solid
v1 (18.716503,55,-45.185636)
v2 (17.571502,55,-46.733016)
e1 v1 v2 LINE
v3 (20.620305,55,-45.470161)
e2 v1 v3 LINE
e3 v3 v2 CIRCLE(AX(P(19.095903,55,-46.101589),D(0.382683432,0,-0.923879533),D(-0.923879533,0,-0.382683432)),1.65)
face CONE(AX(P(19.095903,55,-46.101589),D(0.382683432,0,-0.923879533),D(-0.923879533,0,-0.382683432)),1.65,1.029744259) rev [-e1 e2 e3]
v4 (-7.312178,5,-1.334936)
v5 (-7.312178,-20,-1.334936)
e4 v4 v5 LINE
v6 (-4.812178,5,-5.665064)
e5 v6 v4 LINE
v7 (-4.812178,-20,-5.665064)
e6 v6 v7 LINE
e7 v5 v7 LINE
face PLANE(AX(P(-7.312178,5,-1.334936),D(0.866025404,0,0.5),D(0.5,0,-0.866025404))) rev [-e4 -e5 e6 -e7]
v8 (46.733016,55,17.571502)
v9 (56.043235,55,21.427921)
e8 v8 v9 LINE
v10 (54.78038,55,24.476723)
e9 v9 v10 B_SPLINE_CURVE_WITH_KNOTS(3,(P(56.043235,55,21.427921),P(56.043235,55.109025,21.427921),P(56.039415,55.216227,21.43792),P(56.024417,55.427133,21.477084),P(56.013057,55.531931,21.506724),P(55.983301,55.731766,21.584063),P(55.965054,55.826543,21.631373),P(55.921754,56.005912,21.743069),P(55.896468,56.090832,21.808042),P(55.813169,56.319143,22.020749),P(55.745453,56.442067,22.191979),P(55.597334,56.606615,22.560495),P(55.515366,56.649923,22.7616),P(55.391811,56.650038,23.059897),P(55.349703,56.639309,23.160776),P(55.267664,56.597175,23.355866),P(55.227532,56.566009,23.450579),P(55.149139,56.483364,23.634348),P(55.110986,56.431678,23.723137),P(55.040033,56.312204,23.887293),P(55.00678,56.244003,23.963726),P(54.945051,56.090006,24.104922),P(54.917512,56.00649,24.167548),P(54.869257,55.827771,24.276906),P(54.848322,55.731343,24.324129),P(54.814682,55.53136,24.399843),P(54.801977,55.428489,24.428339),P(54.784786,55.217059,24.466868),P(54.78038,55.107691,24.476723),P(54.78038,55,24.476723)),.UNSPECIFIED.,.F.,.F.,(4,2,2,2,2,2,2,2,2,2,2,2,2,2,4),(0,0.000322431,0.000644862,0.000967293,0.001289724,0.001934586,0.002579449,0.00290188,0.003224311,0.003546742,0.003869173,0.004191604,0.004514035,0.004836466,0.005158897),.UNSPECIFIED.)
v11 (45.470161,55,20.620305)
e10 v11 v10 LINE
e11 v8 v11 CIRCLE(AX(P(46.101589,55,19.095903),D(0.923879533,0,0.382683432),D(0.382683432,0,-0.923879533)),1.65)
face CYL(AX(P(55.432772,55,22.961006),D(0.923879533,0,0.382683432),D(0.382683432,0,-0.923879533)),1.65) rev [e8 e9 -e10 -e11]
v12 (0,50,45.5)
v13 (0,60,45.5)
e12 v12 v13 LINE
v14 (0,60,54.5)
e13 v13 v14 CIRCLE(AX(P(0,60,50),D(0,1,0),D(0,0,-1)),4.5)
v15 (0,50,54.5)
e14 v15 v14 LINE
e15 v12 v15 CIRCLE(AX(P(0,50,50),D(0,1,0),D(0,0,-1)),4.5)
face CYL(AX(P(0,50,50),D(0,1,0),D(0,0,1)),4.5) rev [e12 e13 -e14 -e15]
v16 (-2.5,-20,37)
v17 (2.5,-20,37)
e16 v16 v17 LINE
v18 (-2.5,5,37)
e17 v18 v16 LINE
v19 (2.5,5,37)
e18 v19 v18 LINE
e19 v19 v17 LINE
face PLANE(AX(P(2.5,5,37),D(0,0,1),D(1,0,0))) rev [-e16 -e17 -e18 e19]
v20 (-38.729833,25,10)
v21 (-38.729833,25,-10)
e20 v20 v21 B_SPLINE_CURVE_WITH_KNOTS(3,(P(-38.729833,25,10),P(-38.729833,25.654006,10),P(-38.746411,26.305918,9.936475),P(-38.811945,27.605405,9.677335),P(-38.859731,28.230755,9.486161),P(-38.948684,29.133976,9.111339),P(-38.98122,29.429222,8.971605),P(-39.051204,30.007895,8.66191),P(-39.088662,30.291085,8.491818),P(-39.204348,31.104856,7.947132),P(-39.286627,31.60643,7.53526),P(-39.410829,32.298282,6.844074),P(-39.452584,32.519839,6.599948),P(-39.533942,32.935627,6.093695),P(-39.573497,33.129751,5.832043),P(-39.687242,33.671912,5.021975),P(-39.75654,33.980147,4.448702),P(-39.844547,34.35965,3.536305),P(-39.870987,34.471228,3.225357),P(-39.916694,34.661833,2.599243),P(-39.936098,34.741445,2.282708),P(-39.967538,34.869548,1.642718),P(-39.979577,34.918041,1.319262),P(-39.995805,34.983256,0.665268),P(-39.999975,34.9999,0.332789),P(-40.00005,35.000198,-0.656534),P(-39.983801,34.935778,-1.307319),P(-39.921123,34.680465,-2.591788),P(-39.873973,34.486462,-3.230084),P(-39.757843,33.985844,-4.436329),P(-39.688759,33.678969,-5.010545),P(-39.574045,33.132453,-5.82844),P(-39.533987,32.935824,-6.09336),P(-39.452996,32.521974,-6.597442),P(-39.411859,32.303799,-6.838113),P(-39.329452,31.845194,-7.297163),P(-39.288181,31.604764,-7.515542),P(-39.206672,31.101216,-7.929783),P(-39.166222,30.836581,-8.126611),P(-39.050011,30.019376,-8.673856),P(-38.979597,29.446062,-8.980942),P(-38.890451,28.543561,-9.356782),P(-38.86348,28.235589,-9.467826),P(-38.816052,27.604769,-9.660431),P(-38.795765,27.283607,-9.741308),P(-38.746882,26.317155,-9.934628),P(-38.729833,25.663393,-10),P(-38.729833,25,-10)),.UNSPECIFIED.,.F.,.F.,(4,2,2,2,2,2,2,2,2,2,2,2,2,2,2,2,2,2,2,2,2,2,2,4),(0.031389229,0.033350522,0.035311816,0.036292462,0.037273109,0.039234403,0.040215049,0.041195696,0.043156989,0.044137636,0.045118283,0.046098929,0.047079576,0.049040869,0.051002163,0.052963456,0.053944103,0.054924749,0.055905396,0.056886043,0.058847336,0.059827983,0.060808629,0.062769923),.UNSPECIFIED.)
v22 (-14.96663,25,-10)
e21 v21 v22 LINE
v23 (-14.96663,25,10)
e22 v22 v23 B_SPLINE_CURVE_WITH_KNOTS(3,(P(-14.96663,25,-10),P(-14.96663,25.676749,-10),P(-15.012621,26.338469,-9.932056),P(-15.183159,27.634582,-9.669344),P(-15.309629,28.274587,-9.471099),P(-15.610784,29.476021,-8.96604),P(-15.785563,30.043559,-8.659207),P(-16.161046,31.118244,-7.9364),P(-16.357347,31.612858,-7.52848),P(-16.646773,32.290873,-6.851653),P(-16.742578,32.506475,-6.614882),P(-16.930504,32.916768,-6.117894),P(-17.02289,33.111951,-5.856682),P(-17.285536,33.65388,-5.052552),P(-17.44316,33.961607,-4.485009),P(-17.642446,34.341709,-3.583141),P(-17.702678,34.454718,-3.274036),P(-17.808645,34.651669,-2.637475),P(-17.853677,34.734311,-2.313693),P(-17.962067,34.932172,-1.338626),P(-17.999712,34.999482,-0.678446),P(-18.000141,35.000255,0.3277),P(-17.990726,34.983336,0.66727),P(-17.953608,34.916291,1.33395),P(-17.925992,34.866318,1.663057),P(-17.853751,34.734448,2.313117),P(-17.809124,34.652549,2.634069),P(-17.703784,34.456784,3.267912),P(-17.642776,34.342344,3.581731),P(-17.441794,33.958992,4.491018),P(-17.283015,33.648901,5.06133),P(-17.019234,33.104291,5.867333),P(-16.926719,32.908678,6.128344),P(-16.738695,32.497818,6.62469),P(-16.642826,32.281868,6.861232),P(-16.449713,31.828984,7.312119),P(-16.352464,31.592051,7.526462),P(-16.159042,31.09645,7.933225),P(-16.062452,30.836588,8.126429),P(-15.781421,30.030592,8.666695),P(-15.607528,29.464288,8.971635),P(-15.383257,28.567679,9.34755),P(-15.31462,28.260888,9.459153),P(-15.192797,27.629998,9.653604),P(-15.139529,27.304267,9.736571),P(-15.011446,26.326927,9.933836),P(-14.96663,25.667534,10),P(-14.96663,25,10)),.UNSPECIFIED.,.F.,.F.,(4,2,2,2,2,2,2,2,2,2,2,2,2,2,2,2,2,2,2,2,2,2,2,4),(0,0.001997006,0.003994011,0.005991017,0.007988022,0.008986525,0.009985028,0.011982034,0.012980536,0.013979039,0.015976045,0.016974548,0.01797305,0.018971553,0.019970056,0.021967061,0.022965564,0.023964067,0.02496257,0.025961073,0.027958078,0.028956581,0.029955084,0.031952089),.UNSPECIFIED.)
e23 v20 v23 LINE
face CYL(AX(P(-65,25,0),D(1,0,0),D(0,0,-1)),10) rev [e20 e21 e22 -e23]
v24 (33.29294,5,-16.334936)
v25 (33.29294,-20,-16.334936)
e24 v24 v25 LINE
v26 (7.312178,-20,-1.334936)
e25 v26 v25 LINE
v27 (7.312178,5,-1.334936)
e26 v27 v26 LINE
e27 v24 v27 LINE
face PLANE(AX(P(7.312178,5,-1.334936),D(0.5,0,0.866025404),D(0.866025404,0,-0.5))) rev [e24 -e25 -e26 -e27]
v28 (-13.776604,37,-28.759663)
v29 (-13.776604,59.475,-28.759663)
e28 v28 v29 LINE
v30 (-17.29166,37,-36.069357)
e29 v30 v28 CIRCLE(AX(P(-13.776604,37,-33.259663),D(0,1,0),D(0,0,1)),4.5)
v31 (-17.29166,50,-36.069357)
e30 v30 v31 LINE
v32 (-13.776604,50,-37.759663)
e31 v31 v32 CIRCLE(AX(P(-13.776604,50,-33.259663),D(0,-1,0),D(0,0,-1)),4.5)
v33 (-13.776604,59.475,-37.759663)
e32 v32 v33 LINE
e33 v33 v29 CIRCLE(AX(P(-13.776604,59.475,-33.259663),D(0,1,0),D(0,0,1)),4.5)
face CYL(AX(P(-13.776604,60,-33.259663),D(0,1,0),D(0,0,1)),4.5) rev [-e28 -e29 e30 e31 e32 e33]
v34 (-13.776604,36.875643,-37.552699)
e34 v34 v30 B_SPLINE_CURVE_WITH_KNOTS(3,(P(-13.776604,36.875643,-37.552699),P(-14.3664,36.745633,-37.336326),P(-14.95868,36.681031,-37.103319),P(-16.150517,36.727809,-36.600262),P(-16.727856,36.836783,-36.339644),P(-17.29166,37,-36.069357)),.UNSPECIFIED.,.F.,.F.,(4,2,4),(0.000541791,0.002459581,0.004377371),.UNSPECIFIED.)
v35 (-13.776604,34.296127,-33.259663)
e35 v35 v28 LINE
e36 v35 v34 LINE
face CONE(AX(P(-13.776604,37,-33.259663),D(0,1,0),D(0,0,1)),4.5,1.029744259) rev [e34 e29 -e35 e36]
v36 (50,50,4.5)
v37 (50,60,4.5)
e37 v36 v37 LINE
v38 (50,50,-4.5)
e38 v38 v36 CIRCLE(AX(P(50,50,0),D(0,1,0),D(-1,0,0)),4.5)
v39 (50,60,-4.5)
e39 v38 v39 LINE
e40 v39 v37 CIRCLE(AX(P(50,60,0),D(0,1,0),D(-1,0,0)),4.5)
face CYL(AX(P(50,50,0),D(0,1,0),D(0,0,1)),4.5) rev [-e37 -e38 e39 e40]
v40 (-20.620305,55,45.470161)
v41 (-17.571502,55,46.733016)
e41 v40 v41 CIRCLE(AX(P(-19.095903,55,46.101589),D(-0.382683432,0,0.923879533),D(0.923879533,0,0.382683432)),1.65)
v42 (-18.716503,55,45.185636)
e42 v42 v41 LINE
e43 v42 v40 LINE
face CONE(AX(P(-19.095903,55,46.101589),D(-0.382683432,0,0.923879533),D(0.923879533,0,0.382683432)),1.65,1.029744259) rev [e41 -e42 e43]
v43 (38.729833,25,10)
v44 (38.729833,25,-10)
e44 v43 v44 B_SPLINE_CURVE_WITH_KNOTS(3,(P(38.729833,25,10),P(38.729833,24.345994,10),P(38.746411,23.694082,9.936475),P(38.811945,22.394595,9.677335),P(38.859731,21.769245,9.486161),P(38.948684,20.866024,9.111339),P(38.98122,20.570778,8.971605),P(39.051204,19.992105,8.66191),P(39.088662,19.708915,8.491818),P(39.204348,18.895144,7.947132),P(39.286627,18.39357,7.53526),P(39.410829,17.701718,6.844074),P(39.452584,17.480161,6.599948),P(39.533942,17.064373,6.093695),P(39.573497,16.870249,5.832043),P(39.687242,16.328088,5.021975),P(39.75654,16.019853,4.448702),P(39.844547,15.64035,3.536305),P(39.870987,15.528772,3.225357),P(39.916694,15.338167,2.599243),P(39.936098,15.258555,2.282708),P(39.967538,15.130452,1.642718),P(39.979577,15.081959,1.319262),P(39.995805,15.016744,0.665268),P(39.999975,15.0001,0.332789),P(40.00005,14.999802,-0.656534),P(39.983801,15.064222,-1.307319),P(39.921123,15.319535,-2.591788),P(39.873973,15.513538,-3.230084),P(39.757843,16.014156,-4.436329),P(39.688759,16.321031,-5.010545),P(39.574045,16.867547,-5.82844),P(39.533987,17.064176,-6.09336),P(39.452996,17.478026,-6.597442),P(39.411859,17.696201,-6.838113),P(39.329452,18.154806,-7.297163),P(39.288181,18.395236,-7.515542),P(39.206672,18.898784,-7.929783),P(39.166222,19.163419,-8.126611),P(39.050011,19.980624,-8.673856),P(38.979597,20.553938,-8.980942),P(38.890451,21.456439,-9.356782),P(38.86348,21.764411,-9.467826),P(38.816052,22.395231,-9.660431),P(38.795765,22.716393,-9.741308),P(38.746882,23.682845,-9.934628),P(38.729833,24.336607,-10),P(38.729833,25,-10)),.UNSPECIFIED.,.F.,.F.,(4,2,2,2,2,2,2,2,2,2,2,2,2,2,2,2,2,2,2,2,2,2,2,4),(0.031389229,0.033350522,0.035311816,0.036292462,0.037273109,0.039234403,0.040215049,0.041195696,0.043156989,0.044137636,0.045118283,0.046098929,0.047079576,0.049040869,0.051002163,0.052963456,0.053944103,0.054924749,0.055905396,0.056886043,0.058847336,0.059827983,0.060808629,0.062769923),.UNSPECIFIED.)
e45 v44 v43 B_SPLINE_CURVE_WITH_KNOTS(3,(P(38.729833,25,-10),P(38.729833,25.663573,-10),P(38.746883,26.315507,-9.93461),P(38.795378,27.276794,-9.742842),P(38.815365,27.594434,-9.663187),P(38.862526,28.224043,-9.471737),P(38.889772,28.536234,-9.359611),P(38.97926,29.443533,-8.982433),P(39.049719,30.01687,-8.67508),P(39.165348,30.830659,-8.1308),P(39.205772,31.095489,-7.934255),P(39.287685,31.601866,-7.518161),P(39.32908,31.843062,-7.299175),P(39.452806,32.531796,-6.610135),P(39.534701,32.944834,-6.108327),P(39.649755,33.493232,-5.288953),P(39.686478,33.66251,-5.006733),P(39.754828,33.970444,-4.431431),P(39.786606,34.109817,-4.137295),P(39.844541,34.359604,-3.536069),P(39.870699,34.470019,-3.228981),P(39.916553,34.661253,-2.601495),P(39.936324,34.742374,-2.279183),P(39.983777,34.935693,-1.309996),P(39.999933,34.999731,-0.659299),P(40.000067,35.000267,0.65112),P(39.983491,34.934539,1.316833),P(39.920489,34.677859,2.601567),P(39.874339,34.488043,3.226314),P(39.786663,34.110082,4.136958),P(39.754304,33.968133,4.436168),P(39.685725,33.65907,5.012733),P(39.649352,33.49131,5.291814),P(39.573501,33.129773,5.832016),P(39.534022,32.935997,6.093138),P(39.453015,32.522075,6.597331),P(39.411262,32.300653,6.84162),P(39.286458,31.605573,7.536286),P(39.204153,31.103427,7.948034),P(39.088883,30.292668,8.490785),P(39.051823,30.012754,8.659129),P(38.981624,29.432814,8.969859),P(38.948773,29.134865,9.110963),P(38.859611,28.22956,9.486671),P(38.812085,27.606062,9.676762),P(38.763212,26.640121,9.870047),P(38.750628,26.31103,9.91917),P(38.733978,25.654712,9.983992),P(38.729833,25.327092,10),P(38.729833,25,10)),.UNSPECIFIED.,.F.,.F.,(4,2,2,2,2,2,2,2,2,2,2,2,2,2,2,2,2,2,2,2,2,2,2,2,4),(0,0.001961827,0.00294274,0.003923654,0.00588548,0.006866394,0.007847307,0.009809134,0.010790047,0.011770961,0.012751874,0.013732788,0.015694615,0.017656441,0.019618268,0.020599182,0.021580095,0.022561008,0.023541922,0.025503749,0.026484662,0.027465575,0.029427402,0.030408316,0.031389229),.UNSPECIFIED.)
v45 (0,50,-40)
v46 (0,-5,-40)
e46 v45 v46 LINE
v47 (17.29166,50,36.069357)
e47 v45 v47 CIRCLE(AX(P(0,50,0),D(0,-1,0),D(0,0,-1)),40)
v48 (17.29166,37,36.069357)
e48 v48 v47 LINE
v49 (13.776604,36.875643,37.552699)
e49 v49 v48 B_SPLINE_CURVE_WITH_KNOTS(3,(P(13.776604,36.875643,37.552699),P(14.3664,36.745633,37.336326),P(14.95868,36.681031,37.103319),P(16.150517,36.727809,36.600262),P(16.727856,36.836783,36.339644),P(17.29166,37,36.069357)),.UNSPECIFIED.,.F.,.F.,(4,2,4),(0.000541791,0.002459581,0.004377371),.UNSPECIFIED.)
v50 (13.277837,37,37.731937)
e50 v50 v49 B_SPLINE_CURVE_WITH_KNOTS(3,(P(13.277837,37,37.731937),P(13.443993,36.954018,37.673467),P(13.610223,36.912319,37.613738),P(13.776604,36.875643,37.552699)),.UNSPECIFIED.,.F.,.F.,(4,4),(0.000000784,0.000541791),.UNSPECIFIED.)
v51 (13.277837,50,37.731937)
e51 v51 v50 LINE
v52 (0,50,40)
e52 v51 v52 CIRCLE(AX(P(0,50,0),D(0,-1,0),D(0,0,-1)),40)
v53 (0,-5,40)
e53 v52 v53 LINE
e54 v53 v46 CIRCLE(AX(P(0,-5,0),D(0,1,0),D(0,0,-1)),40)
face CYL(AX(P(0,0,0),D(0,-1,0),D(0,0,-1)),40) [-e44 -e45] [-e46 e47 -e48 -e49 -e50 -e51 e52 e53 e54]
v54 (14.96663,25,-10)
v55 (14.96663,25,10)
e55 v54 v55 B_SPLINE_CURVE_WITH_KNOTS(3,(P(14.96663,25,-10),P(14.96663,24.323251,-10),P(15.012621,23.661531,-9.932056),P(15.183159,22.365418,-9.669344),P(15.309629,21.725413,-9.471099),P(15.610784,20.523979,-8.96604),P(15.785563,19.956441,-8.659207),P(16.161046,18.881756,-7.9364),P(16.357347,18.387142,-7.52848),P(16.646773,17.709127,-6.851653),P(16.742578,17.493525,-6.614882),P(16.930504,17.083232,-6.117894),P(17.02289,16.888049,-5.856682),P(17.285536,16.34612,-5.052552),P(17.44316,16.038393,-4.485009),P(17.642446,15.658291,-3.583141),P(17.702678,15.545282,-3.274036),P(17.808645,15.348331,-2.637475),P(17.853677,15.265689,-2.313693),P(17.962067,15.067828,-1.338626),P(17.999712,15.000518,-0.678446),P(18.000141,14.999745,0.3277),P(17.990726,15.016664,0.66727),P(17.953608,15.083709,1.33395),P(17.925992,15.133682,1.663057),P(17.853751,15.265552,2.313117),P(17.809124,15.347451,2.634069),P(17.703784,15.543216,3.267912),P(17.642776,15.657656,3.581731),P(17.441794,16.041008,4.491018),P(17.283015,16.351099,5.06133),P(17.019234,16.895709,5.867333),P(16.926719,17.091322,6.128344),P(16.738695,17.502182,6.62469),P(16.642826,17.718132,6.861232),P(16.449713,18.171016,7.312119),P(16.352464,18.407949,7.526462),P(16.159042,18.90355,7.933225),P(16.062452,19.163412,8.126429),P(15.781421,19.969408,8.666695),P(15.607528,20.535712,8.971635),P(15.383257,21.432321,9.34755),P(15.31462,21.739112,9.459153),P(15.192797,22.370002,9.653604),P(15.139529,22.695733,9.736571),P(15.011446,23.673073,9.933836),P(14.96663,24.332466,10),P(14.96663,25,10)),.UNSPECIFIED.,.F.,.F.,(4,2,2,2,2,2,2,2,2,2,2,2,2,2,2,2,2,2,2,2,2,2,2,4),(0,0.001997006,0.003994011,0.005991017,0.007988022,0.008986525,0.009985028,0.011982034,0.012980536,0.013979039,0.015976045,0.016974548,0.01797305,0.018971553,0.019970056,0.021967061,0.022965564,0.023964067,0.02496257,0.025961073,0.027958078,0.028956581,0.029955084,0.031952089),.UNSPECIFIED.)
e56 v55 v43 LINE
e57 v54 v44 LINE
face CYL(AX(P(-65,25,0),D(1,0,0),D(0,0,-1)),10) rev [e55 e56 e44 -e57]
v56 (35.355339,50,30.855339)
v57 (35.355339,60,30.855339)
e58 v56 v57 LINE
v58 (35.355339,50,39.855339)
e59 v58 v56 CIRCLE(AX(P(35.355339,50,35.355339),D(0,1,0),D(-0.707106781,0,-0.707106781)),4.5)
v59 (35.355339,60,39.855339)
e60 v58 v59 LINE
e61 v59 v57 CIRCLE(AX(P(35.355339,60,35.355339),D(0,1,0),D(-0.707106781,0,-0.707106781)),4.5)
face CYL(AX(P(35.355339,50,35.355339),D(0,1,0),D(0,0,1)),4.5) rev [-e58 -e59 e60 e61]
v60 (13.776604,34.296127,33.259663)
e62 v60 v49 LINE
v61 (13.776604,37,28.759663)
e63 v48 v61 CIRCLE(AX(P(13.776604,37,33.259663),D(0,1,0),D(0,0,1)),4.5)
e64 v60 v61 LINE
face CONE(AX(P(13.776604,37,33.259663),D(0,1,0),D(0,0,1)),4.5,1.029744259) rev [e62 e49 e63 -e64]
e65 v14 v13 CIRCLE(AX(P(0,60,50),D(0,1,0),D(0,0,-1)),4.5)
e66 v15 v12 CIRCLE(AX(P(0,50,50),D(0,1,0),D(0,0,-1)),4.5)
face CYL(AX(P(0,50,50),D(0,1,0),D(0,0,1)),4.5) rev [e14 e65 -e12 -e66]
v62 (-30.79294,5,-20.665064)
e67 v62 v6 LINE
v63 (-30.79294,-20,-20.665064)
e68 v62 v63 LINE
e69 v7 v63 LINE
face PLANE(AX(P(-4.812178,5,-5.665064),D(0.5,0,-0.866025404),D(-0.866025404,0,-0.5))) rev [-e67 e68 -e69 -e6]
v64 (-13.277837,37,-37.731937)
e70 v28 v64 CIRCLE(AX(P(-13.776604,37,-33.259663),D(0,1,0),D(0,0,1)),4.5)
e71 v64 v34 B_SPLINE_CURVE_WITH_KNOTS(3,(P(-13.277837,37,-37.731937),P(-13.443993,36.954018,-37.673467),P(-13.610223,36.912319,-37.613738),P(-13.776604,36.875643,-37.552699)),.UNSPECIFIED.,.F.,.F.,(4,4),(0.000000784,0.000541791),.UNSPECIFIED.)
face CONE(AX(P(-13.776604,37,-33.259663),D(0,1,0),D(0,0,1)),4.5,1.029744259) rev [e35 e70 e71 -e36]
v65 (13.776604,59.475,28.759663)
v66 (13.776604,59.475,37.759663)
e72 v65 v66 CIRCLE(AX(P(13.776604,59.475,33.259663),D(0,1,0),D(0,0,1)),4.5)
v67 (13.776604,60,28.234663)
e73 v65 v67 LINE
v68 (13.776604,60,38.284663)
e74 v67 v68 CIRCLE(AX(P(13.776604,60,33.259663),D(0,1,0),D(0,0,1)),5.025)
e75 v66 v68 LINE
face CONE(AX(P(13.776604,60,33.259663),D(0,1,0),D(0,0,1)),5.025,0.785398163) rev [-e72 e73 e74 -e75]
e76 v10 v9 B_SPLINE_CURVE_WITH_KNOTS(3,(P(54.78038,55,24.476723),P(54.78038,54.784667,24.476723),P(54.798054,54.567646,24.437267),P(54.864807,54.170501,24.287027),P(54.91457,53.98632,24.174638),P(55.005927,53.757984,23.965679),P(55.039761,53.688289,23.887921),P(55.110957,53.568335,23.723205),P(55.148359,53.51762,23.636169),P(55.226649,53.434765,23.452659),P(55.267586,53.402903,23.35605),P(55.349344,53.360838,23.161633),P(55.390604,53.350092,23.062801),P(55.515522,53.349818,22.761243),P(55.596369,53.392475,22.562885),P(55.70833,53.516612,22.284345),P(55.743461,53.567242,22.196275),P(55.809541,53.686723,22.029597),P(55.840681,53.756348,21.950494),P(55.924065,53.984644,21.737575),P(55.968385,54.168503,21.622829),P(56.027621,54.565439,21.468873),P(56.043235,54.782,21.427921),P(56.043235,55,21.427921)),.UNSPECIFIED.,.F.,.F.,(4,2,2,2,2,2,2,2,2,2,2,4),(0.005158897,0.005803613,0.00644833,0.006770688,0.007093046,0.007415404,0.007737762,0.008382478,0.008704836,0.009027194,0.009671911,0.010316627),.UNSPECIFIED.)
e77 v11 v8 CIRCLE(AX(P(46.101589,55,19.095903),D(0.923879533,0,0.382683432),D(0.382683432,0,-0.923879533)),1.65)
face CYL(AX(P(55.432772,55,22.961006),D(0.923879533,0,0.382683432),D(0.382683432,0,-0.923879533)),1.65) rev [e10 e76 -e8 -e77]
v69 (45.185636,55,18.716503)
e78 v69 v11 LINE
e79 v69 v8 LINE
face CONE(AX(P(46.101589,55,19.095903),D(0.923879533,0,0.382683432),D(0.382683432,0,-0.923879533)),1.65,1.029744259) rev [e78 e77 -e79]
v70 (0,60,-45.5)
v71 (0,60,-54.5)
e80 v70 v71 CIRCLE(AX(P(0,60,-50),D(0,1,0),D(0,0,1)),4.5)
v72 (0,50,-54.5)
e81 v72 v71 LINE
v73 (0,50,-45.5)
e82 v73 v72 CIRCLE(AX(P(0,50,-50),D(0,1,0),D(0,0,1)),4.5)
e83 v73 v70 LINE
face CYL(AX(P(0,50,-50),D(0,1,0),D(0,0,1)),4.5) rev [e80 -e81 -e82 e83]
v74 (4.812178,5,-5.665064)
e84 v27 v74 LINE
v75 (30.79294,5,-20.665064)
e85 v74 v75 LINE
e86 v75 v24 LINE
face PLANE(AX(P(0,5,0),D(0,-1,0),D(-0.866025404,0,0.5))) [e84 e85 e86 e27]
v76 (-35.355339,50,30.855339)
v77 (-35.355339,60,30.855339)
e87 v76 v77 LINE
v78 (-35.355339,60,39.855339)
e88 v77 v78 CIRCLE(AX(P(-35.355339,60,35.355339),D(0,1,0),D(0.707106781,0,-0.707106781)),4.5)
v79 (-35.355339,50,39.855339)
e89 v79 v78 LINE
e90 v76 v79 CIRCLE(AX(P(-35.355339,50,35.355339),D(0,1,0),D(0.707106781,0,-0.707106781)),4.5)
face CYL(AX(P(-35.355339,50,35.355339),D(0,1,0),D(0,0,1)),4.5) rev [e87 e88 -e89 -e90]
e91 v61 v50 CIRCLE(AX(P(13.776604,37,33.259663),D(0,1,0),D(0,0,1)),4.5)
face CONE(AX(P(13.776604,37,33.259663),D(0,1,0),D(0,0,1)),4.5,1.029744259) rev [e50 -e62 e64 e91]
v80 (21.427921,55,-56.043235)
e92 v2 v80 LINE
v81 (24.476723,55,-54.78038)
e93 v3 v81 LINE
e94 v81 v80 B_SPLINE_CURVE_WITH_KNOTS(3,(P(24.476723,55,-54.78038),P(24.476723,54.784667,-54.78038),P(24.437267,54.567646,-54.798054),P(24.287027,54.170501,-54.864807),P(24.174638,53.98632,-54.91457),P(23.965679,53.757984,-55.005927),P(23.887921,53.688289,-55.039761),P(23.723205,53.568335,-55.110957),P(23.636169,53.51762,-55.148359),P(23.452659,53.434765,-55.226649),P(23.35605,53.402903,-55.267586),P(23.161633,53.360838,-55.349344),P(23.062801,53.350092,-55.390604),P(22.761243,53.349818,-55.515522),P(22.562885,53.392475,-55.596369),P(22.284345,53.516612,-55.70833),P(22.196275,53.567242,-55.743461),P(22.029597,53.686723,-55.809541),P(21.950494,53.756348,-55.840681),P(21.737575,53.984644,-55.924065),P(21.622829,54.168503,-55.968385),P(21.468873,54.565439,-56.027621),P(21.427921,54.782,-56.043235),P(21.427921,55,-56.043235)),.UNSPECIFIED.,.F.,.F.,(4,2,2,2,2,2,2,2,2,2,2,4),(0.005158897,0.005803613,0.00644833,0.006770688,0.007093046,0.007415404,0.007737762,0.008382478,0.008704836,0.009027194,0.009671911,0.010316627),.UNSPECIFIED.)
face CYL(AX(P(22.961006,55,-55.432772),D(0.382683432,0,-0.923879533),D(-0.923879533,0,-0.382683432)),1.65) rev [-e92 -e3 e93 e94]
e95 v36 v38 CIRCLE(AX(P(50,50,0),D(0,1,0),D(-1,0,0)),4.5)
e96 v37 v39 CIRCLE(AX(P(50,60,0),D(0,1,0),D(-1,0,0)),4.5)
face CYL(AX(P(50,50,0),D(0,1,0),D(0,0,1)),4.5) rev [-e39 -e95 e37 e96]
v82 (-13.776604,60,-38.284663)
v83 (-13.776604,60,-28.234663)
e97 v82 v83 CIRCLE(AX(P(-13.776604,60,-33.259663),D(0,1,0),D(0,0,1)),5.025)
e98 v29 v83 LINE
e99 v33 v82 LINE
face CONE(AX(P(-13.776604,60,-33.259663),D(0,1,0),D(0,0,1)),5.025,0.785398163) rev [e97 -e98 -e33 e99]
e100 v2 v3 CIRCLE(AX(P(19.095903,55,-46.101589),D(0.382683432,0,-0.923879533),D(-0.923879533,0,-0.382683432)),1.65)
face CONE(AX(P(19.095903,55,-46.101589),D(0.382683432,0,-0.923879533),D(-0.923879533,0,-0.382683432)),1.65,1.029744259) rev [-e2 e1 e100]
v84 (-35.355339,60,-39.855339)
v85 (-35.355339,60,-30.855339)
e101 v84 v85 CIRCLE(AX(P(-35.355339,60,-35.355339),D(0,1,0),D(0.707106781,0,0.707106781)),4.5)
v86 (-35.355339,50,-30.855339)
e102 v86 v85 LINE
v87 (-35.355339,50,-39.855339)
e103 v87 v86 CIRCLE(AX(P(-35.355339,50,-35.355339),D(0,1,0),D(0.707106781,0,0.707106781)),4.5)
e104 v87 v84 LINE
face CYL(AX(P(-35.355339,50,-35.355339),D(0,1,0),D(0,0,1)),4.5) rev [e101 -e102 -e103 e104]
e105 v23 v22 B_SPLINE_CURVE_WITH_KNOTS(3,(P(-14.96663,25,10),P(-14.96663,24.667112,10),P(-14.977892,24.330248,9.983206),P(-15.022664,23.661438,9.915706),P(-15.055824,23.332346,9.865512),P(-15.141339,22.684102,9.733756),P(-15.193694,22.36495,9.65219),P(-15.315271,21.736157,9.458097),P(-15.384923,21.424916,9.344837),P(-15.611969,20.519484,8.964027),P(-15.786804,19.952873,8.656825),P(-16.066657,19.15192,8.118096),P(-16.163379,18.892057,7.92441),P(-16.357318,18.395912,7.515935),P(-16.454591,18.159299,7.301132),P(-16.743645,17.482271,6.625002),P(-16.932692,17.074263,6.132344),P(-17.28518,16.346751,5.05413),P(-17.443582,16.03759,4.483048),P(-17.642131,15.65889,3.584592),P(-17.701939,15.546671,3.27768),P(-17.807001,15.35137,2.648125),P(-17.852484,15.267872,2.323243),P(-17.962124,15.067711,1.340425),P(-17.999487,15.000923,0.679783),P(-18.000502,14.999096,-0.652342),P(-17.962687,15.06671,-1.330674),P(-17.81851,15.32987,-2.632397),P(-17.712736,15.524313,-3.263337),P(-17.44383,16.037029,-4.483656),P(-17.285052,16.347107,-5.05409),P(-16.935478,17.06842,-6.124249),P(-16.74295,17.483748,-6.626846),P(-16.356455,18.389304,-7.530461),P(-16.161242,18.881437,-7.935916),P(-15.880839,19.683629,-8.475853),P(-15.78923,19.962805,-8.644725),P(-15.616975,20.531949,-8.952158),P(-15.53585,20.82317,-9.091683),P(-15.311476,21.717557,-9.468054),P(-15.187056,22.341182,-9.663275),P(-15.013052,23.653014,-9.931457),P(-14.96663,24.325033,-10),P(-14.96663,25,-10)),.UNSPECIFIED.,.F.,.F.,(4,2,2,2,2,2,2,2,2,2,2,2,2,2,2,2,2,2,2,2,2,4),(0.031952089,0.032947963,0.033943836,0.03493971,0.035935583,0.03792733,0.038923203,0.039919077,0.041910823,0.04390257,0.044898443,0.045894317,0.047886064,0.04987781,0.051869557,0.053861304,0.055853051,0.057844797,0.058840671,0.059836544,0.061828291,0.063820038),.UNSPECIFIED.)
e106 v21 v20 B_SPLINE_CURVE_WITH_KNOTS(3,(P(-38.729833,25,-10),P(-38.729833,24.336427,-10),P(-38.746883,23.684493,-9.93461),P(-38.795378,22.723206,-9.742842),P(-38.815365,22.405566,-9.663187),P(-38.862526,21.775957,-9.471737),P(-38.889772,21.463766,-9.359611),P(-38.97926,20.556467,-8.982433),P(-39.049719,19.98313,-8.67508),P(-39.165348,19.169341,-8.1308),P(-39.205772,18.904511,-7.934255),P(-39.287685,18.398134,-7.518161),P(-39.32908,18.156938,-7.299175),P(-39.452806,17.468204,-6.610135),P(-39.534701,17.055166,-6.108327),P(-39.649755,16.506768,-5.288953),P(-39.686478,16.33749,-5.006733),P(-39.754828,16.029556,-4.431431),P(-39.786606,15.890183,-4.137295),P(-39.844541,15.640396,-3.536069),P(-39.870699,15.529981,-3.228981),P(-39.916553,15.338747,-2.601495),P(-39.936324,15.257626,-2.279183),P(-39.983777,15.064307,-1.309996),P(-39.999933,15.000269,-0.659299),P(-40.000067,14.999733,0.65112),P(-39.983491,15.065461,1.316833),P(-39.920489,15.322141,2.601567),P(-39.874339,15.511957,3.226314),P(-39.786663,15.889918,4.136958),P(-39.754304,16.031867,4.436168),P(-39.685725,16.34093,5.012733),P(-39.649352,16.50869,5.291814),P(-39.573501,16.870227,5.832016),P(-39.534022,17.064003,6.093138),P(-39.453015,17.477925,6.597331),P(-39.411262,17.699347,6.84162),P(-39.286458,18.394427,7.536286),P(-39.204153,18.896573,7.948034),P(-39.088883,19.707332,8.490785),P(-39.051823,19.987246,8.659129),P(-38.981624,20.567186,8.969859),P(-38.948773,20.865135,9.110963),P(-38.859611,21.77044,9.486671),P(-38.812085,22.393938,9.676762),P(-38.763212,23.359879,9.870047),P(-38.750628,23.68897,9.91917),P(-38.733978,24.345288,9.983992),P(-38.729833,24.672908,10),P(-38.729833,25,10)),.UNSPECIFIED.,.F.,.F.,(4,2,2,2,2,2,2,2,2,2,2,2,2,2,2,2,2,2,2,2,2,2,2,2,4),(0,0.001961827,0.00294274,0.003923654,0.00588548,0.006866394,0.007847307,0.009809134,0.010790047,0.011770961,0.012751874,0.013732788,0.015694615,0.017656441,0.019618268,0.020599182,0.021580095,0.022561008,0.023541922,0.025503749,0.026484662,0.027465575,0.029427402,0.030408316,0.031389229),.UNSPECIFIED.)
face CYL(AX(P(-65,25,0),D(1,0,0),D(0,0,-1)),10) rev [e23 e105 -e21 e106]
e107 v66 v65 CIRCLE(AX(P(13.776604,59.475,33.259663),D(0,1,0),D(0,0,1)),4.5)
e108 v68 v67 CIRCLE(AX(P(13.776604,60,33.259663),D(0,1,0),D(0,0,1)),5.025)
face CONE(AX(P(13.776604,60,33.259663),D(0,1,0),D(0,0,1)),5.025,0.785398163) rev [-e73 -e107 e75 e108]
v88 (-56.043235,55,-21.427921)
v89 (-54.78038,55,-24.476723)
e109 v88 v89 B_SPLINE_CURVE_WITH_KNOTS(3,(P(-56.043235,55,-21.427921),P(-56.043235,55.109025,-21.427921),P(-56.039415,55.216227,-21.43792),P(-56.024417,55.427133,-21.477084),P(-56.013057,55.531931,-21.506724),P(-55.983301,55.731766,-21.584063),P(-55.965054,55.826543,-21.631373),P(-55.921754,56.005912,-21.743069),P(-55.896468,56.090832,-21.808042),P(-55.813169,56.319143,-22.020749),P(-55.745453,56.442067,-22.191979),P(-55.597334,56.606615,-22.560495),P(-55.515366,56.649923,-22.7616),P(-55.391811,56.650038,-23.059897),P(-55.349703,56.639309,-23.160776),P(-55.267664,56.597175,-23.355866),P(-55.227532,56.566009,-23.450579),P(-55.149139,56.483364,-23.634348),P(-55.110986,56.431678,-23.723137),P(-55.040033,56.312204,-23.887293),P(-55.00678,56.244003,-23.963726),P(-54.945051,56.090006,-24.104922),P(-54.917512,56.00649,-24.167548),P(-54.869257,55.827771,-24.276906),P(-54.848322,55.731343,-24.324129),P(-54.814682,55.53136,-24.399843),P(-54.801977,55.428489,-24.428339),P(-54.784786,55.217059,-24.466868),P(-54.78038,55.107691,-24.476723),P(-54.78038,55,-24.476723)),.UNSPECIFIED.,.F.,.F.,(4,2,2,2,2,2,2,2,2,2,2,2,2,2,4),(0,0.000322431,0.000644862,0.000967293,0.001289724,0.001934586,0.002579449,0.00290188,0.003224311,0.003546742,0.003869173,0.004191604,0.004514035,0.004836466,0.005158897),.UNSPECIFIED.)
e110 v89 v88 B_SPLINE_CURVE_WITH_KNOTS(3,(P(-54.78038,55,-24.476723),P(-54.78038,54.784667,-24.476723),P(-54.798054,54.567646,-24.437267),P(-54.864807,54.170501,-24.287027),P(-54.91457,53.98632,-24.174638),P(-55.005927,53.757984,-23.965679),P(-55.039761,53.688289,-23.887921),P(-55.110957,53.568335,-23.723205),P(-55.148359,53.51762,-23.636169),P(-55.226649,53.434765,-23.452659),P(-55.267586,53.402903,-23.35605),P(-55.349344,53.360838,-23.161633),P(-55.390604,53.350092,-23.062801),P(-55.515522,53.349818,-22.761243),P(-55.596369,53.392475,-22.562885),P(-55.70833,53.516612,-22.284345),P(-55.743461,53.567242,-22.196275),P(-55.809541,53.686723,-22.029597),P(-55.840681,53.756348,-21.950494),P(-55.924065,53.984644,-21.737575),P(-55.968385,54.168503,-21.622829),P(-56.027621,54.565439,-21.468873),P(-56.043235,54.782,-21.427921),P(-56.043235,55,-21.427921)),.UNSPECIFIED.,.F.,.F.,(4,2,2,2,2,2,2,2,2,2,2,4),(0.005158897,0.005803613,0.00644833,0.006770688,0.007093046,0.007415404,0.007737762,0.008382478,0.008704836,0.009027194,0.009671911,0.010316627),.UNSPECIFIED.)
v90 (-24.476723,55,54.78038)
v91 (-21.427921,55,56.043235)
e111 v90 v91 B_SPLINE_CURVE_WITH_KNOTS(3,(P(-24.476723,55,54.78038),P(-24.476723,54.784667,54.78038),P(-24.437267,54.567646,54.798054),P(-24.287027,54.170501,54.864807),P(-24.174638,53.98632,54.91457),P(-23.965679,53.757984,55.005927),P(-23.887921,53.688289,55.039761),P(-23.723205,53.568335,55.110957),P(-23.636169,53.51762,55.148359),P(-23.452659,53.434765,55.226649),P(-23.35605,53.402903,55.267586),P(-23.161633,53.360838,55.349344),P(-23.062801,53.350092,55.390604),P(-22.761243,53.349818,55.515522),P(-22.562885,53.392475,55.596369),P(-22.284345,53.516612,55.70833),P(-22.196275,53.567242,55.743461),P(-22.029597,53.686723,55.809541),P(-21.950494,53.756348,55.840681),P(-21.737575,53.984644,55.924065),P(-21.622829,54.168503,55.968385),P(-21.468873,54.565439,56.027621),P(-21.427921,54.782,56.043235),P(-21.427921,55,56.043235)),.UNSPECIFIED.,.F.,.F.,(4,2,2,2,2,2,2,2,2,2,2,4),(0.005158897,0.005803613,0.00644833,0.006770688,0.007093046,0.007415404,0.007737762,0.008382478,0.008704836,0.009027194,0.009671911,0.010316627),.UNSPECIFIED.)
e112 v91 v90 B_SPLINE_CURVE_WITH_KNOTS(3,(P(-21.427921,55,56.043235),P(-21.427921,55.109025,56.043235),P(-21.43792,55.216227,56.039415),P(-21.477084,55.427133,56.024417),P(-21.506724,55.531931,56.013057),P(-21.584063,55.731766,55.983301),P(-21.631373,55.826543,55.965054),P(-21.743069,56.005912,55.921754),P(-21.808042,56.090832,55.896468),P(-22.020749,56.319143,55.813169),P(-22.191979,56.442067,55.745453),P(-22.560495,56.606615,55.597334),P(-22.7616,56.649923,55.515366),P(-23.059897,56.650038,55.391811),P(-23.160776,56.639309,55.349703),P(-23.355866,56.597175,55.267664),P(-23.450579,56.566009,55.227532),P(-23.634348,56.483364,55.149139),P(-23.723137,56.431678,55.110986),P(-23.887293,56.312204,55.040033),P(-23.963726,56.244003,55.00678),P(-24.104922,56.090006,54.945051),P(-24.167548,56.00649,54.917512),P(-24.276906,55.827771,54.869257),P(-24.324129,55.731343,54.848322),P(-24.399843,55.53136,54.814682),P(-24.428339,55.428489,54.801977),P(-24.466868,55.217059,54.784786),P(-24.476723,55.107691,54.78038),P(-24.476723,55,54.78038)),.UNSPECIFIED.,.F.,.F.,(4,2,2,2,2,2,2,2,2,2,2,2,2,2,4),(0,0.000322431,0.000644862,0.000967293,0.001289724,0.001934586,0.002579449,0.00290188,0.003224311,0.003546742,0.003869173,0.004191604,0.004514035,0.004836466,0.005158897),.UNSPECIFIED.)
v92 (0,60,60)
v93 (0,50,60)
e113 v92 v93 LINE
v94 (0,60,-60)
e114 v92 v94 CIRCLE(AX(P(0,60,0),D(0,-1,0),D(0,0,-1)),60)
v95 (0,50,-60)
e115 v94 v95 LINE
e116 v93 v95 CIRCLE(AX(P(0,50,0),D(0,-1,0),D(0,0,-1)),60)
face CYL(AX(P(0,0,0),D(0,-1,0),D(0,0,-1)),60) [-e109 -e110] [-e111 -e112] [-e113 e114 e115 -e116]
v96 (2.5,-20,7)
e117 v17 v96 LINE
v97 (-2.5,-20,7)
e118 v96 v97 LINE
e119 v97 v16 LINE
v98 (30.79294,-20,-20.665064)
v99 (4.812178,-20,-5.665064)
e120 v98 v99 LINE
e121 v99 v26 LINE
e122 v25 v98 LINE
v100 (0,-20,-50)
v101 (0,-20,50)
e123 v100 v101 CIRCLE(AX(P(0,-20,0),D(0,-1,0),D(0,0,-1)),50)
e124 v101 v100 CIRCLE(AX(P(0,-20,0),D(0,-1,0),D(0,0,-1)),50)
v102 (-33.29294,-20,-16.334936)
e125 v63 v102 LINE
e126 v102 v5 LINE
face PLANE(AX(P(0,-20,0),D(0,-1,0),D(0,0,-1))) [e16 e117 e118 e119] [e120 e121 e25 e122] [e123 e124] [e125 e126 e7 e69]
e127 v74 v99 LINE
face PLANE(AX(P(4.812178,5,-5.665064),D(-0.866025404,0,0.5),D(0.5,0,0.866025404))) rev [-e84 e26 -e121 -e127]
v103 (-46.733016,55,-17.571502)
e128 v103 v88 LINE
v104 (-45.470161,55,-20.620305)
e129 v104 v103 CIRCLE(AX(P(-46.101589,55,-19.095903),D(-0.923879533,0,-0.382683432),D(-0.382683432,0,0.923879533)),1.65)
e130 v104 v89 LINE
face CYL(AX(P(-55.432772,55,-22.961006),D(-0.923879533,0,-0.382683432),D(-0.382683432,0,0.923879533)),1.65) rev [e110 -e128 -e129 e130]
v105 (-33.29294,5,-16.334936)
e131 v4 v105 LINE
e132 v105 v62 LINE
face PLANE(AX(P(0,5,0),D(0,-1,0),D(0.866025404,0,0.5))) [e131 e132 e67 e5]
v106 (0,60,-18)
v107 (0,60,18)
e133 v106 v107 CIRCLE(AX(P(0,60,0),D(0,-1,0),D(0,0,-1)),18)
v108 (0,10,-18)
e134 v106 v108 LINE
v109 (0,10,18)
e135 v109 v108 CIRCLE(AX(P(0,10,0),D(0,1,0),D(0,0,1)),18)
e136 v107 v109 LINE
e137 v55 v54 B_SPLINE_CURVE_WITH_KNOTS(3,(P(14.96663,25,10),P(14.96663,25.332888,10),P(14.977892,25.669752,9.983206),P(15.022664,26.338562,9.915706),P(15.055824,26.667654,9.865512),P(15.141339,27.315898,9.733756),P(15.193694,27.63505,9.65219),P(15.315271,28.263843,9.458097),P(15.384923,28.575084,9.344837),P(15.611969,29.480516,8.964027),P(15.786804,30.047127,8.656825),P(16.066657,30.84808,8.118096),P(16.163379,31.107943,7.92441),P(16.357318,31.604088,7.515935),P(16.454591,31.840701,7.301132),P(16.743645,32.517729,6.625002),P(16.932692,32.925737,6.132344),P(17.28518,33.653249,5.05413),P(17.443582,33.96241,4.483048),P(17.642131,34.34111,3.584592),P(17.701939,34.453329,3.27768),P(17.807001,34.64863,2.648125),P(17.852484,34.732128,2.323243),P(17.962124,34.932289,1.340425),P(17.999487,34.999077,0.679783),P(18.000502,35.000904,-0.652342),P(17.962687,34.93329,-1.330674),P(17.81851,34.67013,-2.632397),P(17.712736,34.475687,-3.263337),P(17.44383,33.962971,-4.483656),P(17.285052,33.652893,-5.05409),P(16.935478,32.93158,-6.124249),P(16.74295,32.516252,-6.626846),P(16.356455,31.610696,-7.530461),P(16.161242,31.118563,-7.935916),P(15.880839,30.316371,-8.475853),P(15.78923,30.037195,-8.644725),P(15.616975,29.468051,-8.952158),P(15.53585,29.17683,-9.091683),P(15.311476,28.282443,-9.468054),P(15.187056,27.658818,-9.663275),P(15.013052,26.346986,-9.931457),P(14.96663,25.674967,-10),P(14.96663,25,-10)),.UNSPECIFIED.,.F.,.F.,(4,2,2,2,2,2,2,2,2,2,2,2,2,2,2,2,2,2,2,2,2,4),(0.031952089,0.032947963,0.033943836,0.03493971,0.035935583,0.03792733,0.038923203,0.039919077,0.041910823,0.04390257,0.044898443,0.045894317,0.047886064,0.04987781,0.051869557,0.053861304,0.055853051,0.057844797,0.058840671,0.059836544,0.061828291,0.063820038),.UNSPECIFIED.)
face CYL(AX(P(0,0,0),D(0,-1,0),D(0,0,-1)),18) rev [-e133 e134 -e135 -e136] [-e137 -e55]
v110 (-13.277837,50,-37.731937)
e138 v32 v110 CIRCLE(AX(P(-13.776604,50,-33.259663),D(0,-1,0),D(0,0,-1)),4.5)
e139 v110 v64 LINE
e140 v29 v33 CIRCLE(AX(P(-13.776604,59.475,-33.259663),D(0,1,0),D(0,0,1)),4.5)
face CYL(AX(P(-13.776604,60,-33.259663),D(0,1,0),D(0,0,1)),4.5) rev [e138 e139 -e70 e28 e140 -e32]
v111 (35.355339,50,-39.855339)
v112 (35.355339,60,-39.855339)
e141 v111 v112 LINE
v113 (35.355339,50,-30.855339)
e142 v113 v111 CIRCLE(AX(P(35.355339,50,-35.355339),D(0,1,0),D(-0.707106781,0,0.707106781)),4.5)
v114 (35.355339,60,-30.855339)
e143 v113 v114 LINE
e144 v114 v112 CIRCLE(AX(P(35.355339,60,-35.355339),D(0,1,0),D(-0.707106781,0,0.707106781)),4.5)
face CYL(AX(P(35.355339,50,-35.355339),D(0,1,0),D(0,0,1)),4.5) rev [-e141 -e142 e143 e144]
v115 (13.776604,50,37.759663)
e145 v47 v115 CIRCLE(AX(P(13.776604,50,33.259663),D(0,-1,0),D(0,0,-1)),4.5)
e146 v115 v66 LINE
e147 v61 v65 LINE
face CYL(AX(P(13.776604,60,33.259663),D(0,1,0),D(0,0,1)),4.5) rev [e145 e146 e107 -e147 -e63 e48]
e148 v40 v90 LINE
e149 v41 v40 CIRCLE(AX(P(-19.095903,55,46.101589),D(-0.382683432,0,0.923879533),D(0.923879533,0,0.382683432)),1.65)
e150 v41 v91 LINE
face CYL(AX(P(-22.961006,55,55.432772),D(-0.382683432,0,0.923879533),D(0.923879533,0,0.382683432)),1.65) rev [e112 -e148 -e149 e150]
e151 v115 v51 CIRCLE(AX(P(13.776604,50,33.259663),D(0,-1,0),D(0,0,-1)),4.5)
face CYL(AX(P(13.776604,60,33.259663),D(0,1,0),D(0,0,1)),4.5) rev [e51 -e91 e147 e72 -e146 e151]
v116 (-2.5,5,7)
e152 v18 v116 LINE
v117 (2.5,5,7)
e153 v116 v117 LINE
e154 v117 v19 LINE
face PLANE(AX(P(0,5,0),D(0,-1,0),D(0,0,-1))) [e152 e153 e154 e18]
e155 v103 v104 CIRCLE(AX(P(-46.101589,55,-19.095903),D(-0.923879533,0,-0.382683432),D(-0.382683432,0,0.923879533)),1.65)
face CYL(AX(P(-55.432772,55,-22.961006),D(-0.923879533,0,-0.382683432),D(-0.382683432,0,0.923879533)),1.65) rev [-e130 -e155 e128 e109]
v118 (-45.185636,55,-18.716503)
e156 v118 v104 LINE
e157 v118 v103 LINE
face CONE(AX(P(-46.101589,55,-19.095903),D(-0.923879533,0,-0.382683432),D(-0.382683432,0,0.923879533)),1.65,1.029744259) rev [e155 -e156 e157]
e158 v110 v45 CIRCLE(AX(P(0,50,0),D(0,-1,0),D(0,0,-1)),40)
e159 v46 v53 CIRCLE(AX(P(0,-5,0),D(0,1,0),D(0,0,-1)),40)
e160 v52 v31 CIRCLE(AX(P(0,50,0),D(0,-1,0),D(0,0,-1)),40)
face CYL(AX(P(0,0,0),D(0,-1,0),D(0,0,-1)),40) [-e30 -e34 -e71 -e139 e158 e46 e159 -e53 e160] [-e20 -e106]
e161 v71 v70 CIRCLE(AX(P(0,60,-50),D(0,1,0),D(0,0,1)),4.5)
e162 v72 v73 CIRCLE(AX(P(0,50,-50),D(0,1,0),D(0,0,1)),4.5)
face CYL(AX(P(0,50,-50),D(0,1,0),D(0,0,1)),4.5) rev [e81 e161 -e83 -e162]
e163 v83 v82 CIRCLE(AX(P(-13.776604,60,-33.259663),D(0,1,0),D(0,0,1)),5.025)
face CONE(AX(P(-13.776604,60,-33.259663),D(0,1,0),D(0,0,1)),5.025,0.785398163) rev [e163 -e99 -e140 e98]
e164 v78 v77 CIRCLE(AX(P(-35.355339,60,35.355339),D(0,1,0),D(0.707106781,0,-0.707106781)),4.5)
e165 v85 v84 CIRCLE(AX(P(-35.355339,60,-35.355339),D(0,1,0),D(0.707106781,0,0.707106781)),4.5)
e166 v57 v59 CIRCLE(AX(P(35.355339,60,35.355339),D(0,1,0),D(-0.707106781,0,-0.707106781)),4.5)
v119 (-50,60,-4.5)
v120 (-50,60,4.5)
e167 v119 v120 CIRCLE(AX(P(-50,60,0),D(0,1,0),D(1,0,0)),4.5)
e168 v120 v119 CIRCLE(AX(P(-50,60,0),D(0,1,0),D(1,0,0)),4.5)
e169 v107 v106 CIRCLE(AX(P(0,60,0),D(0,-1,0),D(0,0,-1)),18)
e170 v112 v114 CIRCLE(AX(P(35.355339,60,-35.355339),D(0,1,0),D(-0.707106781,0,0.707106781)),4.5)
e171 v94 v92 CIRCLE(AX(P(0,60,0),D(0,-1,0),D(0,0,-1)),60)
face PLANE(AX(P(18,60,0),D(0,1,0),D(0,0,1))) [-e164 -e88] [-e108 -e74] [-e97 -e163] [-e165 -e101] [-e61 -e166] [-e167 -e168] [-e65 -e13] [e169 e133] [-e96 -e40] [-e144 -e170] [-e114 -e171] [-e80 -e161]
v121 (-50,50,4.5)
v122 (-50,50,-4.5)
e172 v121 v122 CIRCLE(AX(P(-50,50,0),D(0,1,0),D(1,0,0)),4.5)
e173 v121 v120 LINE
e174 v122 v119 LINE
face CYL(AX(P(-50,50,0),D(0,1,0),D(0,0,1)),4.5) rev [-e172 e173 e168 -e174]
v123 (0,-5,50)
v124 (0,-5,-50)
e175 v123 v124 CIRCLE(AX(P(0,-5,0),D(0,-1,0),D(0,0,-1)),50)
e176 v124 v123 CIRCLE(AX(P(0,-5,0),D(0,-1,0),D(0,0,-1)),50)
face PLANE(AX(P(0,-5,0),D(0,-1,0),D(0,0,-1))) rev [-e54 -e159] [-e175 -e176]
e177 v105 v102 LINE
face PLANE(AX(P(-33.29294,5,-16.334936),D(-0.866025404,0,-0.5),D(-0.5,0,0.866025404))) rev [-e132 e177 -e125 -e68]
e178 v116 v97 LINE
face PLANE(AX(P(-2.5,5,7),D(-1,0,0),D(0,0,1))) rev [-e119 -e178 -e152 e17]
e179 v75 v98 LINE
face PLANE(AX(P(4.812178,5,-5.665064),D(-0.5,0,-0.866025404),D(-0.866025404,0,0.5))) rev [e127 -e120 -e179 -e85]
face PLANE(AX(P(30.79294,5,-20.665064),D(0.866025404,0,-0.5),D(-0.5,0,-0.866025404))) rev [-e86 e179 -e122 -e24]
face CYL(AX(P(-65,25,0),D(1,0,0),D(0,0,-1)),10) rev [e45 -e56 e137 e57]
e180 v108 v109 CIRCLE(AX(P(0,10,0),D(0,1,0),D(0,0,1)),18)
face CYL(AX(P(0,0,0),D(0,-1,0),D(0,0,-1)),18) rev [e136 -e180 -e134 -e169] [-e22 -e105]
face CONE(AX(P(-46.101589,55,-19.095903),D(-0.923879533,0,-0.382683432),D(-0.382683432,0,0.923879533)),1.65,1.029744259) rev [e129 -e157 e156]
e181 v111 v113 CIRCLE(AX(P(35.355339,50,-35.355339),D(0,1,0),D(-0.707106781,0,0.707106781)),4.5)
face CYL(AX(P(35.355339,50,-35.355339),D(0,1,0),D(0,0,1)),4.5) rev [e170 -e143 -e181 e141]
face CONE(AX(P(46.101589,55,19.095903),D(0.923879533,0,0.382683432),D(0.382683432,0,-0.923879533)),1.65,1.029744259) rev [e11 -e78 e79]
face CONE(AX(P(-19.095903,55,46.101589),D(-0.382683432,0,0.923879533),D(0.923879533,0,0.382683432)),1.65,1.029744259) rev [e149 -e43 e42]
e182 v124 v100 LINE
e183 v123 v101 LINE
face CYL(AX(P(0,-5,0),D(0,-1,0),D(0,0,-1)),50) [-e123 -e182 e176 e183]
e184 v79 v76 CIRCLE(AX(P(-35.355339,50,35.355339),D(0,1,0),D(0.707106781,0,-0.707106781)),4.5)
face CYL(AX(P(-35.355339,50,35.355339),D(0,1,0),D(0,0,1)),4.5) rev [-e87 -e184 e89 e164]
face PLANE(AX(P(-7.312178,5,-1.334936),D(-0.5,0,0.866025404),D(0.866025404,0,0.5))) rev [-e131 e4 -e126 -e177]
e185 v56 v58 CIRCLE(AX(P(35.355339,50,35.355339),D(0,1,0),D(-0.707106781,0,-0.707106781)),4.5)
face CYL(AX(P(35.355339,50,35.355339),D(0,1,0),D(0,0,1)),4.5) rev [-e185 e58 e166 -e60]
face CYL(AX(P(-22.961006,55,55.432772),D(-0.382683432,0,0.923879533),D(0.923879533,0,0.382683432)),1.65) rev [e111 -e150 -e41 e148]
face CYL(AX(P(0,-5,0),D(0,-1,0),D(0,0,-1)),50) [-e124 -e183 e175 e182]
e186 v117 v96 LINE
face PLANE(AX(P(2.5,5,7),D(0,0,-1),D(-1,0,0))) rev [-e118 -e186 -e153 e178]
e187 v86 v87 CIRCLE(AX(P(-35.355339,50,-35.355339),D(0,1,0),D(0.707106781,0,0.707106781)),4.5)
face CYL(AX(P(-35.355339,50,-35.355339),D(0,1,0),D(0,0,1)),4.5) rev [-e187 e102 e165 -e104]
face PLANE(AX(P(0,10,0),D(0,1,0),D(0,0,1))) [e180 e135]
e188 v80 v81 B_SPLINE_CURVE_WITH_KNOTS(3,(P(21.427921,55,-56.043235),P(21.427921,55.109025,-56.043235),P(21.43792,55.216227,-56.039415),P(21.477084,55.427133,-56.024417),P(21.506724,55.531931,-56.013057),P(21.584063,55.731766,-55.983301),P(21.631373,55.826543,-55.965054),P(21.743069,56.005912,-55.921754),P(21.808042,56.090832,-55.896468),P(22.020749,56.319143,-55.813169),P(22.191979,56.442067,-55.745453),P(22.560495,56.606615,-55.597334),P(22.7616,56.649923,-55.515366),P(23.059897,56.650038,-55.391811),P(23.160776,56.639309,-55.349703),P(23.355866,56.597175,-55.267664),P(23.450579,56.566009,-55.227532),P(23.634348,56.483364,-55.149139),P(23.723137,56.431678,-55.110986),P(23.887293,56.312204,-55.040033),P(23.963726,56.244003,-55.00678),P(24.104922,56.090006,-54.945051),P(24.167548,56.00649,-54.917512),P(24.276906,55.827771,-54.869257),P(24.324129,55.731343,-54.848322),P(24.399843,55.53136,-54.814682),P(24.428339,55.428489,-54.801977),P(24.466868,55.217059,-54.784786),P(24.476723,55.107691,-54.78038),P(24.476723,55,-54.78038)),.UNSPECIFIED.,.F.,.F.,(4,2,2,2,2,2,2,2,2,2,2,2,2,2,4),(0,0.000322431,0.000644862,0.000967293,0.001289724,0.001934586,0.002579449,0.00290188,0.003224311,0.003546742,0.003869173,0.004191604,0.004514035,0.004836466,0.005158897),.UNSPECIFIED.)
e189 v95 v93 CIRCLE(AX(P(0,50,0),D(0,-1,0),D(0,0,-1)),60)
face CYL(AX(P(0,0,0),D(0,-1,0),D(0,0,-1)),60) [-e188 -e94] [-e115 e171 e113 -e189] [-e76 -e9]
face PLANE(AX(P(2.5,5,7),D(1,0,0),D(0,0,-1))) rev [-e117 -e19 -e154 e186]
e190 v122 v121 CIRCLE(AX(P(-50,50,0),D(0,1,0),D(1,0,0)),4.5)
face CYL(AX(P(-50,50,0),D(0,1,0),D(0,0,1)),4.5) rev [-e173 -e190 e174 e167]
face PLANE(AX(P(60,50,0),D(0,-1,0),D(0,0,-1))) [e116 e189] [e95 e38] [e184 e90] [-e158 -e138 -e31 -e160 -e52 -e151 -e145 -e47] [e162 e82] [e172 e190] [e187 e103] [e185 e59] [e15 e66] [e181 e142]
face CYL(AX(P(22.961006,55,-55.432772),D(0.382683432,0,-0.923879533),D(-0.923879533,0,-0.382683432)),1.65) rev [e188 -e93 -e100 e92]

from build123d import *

# Parameters (mm, degrees)
SKETCH_2_R               = 4.5
CUT_EXTRUDE_1_DEPTH      = 10
PATTERN_CIRCULAR_1_COUNT = 8
EXTRUDE_START            = 10
SKETCH_3_R               = 40
EXTRUDE_1_DEPTH          = 10
SKETCH_7_R               = 18
EXTRUDE_2_DEPTH          = 10
SKETCH_5_W               = 5
SKETCH_5_H               = 30
CUT_EXTRUDE_2_DEPTH      = 15
PATTERN_CIRCULAR_3_COUNT = 3
PATTERN_CIRCULAR_4_COUNT = 4
EXTRUDE_3_DEPTH          = 10
EXTRUDE_3_DEPTH_BACK     = 5
SKETCH_11_R              = 50
SKETCH_11_W              = 5
SKETCH_11_H              = 30
M10X1_0_1_D              = 9
M10X1_0_1_DEPTH          = 23
M10X1_0_1_CSINK_D        = 10.05
M10X1_0_1_CSINK_ANGLE    = 90
M10X1_0_1_TIP            = 2.703872786
SKETCH_16_R              = 10
CUT_EXTRUDE_3_DEPTH      = 65


with BuildPart() as part:
    # 草图1 → 旋转1 (revolve)
    with BuildSketch(Plane.XY, mode=Mode.PRIVATE) as revolve_1_sk:
        Polygon((18, 60), (60, 60), (60, 50), (40, 50), (40, 0), (18, 0), align=None)
    revolve(revolve_1_sk.sketch.rotate(Axis((0, 0, 0), (0, 1, 0)), 90), axis=Axis((0, 0, 0), (0, 1, 0)))

    # 草图2 → 切除-拉伸1 (cut)
    with BuildSketch(Plane(origin=(0, 60, 0), x_dir=(1, 0, 0), z_dir=(0, 1, 0))):
        with Locations(Location((0, 50, 0), (0, 0, 270))):
            Circle(SKETCH_2_R)
    cut_extrude_1 = extrude(amount=-CUT_EXTRUDE_1_DEPTH, mode=Mode.SUBTRACT)

    # 阵列(圆周)1: 切除-拉伸1 ×8 about axis
    pattern_circular_1_axis = Axis((0, 0, 0), (0, 1, 0))
    for i in range(1, PATTERN_CIRCULAR_1_COUNT):
        add(cut_extrude_1.rotate(pattern_circular_1_axis, i * 360 / PATTERN_CIRCULAR_1_COUNT), mode=Mode.SUBTRACT)

    # 草图3 → 凸台-拉伸1 (add)
    with BuildSketch(Plane.XZ.offset(EXTRUDE_START)):
        with Locations(Location((0, 0, 0), (0, 0, 270))):
            Circle(SKETCH_3_R)
    extrude(amount=-EXTRUDE_1_DEPTH)

    # 草图7 → 凸台-拉伸2 (add)
    with BuildSketch(Plane(origin=(0, 0, 0), x_dir=(1, 0, 0), z_dir=(0, 1, 0)).offset(EXTRUDE_START)):
        with Locations(Location((0, 0, 0), (0, 0, 90))):
            Circle(SKETCH_7_R)
    extrude(amount=-EXTRUDE_2_DEPTH)

    # 草图5 → 切除-拉伸2 (cut)
    with BuildSketch(Plane.XZ.offset(10)):
        with Locations((0, 22)):
            Rectangle(SKETCH_5_W, SKETCH_5_H)
    cut_extrude_2 = extrude(amount=-CUT_EXTRUDE_2_DEPTH, mode=Mode.SUBTRACT)

    # 阵列(圆周)3: 切除-拉伸2 ×3 about axis
    pattern_circular_3_axis = Axis((0, 0, 0), (0, 1, 0))
    for i in range(1, PATTERN_CIRCULAR_3_COUNT):
        add(cut_extrude_2.rotate(pattern_circular_3_axis, i * 360 / PATTERN_CIRCULAR_3_COUNT), mode=Mode.SUBTRACT)

    # 草图10 → M4x0.7 螺纹孔1 (revolve, cut)
    with BuildSketch(Plane(origin=(22.961005942, 55, -55.432771951), x_dir=(-0.9238795325112892, 0, -0.3826834323650839), z_dir=(0, 1, 0))):
        Polygon((0, 0), (0, 11.091420021), (1.65, 10.1), (1.65, 0), align=None)
    m4x0_7_1 = revolve(axis=Axis((25.391045737, 55, -61.299406982), (-0.3826834323650839, 0, 0.9238795325112892)), mode=Mode.SUBTRACT)

    # 阵列(圆周)4: M4x0.7 螺纹孔1 ×4 about axis
    pattern_circular_4_axis = Axis((0, 0, 0), (0, -1, 0))
    for i in range(1, PATTERN_CIRCULAR_4_COUNT):
        add(m4x0_7_1.rotate(pattern_circular_4_axis, i * 360 / PATTERN_CIRCULAR_4_COUNT), mode=Mode.SUBTRACT)

    # 草图11 → 凸台-拉伸3 (add, two sides: drawn at the far end of the back side and taken through both)
    with BuildSketch(Plane.XZ.offset(10).offset(-EXTRUDE_3_DEPTH_BACK)):
        with Locations(Location((0, 0, 0), (0, 0, 270))):
            Circle(SKETCH_11_R)
        with Locations((0, 22)):
            Rectangle(SKETCH_11_W, SKETCH_11_H, mode=Mode.SUBTRACT)
        Polygon((-4.812177826, -5.665063509), (-30.79293994, -20.665063509), (-33.29293994, -16.334936491), (-7.312177826, -1.334936491), align=None, mode=Mode.SUBTRACT)
        Polygon((7.312177826, -1.334936491), (33.29293994, -16.334936491), (30.79293994, -20.665063509), (4.812177826, -5.665063509), align=None, mode=Mode.SUBTRACT)
    extrude(amount=EXTRUDE_3_DEPTH + EXTRUDE_3_DEPTH_BACK)

    # M10x1.0 螺纹孔1
    with Locations(Plane(origin=(-13.776603565, 60, -33.25966317), x_dir=(0, 0, 1), z_dir=(0, 1, 0))):
        with Locations((0, 0), (66.51932634, 27.55320713)):
            CounterSinkHole(M10X1_0_1_D / 2, M10X1_0_1_CSINK_D / 2, depth=M10X1_0_1_DEPTH, counter_sink_angle=M10X1_0_1_CSINK_ANGLE)
            with Locations((0, 0, -(M10X1_0_1_DEPTH + M10X1_0_1_TIP / 2))):  # 118° drill point
                Cone(0, M10X1_0_1_D / 2, M10X1_0_1_TIP, mode=Mode.SUBTRACT)

    # 草图16 → 切除-拉伸3 (cut, symmetric)
    with BuildSketch(Plane(origin=(0, 0, 0), x_dir=(0, 0, -1), z_dir=(1, 0, 0))):
        with Locations((0, 25)):
            Circle(SKETCH_16_R)
    extrude(amount=CUT_EXTRUDE_3_DEPTH, both=True, mode=Mode.SUBTRACT)


solid = part.part
